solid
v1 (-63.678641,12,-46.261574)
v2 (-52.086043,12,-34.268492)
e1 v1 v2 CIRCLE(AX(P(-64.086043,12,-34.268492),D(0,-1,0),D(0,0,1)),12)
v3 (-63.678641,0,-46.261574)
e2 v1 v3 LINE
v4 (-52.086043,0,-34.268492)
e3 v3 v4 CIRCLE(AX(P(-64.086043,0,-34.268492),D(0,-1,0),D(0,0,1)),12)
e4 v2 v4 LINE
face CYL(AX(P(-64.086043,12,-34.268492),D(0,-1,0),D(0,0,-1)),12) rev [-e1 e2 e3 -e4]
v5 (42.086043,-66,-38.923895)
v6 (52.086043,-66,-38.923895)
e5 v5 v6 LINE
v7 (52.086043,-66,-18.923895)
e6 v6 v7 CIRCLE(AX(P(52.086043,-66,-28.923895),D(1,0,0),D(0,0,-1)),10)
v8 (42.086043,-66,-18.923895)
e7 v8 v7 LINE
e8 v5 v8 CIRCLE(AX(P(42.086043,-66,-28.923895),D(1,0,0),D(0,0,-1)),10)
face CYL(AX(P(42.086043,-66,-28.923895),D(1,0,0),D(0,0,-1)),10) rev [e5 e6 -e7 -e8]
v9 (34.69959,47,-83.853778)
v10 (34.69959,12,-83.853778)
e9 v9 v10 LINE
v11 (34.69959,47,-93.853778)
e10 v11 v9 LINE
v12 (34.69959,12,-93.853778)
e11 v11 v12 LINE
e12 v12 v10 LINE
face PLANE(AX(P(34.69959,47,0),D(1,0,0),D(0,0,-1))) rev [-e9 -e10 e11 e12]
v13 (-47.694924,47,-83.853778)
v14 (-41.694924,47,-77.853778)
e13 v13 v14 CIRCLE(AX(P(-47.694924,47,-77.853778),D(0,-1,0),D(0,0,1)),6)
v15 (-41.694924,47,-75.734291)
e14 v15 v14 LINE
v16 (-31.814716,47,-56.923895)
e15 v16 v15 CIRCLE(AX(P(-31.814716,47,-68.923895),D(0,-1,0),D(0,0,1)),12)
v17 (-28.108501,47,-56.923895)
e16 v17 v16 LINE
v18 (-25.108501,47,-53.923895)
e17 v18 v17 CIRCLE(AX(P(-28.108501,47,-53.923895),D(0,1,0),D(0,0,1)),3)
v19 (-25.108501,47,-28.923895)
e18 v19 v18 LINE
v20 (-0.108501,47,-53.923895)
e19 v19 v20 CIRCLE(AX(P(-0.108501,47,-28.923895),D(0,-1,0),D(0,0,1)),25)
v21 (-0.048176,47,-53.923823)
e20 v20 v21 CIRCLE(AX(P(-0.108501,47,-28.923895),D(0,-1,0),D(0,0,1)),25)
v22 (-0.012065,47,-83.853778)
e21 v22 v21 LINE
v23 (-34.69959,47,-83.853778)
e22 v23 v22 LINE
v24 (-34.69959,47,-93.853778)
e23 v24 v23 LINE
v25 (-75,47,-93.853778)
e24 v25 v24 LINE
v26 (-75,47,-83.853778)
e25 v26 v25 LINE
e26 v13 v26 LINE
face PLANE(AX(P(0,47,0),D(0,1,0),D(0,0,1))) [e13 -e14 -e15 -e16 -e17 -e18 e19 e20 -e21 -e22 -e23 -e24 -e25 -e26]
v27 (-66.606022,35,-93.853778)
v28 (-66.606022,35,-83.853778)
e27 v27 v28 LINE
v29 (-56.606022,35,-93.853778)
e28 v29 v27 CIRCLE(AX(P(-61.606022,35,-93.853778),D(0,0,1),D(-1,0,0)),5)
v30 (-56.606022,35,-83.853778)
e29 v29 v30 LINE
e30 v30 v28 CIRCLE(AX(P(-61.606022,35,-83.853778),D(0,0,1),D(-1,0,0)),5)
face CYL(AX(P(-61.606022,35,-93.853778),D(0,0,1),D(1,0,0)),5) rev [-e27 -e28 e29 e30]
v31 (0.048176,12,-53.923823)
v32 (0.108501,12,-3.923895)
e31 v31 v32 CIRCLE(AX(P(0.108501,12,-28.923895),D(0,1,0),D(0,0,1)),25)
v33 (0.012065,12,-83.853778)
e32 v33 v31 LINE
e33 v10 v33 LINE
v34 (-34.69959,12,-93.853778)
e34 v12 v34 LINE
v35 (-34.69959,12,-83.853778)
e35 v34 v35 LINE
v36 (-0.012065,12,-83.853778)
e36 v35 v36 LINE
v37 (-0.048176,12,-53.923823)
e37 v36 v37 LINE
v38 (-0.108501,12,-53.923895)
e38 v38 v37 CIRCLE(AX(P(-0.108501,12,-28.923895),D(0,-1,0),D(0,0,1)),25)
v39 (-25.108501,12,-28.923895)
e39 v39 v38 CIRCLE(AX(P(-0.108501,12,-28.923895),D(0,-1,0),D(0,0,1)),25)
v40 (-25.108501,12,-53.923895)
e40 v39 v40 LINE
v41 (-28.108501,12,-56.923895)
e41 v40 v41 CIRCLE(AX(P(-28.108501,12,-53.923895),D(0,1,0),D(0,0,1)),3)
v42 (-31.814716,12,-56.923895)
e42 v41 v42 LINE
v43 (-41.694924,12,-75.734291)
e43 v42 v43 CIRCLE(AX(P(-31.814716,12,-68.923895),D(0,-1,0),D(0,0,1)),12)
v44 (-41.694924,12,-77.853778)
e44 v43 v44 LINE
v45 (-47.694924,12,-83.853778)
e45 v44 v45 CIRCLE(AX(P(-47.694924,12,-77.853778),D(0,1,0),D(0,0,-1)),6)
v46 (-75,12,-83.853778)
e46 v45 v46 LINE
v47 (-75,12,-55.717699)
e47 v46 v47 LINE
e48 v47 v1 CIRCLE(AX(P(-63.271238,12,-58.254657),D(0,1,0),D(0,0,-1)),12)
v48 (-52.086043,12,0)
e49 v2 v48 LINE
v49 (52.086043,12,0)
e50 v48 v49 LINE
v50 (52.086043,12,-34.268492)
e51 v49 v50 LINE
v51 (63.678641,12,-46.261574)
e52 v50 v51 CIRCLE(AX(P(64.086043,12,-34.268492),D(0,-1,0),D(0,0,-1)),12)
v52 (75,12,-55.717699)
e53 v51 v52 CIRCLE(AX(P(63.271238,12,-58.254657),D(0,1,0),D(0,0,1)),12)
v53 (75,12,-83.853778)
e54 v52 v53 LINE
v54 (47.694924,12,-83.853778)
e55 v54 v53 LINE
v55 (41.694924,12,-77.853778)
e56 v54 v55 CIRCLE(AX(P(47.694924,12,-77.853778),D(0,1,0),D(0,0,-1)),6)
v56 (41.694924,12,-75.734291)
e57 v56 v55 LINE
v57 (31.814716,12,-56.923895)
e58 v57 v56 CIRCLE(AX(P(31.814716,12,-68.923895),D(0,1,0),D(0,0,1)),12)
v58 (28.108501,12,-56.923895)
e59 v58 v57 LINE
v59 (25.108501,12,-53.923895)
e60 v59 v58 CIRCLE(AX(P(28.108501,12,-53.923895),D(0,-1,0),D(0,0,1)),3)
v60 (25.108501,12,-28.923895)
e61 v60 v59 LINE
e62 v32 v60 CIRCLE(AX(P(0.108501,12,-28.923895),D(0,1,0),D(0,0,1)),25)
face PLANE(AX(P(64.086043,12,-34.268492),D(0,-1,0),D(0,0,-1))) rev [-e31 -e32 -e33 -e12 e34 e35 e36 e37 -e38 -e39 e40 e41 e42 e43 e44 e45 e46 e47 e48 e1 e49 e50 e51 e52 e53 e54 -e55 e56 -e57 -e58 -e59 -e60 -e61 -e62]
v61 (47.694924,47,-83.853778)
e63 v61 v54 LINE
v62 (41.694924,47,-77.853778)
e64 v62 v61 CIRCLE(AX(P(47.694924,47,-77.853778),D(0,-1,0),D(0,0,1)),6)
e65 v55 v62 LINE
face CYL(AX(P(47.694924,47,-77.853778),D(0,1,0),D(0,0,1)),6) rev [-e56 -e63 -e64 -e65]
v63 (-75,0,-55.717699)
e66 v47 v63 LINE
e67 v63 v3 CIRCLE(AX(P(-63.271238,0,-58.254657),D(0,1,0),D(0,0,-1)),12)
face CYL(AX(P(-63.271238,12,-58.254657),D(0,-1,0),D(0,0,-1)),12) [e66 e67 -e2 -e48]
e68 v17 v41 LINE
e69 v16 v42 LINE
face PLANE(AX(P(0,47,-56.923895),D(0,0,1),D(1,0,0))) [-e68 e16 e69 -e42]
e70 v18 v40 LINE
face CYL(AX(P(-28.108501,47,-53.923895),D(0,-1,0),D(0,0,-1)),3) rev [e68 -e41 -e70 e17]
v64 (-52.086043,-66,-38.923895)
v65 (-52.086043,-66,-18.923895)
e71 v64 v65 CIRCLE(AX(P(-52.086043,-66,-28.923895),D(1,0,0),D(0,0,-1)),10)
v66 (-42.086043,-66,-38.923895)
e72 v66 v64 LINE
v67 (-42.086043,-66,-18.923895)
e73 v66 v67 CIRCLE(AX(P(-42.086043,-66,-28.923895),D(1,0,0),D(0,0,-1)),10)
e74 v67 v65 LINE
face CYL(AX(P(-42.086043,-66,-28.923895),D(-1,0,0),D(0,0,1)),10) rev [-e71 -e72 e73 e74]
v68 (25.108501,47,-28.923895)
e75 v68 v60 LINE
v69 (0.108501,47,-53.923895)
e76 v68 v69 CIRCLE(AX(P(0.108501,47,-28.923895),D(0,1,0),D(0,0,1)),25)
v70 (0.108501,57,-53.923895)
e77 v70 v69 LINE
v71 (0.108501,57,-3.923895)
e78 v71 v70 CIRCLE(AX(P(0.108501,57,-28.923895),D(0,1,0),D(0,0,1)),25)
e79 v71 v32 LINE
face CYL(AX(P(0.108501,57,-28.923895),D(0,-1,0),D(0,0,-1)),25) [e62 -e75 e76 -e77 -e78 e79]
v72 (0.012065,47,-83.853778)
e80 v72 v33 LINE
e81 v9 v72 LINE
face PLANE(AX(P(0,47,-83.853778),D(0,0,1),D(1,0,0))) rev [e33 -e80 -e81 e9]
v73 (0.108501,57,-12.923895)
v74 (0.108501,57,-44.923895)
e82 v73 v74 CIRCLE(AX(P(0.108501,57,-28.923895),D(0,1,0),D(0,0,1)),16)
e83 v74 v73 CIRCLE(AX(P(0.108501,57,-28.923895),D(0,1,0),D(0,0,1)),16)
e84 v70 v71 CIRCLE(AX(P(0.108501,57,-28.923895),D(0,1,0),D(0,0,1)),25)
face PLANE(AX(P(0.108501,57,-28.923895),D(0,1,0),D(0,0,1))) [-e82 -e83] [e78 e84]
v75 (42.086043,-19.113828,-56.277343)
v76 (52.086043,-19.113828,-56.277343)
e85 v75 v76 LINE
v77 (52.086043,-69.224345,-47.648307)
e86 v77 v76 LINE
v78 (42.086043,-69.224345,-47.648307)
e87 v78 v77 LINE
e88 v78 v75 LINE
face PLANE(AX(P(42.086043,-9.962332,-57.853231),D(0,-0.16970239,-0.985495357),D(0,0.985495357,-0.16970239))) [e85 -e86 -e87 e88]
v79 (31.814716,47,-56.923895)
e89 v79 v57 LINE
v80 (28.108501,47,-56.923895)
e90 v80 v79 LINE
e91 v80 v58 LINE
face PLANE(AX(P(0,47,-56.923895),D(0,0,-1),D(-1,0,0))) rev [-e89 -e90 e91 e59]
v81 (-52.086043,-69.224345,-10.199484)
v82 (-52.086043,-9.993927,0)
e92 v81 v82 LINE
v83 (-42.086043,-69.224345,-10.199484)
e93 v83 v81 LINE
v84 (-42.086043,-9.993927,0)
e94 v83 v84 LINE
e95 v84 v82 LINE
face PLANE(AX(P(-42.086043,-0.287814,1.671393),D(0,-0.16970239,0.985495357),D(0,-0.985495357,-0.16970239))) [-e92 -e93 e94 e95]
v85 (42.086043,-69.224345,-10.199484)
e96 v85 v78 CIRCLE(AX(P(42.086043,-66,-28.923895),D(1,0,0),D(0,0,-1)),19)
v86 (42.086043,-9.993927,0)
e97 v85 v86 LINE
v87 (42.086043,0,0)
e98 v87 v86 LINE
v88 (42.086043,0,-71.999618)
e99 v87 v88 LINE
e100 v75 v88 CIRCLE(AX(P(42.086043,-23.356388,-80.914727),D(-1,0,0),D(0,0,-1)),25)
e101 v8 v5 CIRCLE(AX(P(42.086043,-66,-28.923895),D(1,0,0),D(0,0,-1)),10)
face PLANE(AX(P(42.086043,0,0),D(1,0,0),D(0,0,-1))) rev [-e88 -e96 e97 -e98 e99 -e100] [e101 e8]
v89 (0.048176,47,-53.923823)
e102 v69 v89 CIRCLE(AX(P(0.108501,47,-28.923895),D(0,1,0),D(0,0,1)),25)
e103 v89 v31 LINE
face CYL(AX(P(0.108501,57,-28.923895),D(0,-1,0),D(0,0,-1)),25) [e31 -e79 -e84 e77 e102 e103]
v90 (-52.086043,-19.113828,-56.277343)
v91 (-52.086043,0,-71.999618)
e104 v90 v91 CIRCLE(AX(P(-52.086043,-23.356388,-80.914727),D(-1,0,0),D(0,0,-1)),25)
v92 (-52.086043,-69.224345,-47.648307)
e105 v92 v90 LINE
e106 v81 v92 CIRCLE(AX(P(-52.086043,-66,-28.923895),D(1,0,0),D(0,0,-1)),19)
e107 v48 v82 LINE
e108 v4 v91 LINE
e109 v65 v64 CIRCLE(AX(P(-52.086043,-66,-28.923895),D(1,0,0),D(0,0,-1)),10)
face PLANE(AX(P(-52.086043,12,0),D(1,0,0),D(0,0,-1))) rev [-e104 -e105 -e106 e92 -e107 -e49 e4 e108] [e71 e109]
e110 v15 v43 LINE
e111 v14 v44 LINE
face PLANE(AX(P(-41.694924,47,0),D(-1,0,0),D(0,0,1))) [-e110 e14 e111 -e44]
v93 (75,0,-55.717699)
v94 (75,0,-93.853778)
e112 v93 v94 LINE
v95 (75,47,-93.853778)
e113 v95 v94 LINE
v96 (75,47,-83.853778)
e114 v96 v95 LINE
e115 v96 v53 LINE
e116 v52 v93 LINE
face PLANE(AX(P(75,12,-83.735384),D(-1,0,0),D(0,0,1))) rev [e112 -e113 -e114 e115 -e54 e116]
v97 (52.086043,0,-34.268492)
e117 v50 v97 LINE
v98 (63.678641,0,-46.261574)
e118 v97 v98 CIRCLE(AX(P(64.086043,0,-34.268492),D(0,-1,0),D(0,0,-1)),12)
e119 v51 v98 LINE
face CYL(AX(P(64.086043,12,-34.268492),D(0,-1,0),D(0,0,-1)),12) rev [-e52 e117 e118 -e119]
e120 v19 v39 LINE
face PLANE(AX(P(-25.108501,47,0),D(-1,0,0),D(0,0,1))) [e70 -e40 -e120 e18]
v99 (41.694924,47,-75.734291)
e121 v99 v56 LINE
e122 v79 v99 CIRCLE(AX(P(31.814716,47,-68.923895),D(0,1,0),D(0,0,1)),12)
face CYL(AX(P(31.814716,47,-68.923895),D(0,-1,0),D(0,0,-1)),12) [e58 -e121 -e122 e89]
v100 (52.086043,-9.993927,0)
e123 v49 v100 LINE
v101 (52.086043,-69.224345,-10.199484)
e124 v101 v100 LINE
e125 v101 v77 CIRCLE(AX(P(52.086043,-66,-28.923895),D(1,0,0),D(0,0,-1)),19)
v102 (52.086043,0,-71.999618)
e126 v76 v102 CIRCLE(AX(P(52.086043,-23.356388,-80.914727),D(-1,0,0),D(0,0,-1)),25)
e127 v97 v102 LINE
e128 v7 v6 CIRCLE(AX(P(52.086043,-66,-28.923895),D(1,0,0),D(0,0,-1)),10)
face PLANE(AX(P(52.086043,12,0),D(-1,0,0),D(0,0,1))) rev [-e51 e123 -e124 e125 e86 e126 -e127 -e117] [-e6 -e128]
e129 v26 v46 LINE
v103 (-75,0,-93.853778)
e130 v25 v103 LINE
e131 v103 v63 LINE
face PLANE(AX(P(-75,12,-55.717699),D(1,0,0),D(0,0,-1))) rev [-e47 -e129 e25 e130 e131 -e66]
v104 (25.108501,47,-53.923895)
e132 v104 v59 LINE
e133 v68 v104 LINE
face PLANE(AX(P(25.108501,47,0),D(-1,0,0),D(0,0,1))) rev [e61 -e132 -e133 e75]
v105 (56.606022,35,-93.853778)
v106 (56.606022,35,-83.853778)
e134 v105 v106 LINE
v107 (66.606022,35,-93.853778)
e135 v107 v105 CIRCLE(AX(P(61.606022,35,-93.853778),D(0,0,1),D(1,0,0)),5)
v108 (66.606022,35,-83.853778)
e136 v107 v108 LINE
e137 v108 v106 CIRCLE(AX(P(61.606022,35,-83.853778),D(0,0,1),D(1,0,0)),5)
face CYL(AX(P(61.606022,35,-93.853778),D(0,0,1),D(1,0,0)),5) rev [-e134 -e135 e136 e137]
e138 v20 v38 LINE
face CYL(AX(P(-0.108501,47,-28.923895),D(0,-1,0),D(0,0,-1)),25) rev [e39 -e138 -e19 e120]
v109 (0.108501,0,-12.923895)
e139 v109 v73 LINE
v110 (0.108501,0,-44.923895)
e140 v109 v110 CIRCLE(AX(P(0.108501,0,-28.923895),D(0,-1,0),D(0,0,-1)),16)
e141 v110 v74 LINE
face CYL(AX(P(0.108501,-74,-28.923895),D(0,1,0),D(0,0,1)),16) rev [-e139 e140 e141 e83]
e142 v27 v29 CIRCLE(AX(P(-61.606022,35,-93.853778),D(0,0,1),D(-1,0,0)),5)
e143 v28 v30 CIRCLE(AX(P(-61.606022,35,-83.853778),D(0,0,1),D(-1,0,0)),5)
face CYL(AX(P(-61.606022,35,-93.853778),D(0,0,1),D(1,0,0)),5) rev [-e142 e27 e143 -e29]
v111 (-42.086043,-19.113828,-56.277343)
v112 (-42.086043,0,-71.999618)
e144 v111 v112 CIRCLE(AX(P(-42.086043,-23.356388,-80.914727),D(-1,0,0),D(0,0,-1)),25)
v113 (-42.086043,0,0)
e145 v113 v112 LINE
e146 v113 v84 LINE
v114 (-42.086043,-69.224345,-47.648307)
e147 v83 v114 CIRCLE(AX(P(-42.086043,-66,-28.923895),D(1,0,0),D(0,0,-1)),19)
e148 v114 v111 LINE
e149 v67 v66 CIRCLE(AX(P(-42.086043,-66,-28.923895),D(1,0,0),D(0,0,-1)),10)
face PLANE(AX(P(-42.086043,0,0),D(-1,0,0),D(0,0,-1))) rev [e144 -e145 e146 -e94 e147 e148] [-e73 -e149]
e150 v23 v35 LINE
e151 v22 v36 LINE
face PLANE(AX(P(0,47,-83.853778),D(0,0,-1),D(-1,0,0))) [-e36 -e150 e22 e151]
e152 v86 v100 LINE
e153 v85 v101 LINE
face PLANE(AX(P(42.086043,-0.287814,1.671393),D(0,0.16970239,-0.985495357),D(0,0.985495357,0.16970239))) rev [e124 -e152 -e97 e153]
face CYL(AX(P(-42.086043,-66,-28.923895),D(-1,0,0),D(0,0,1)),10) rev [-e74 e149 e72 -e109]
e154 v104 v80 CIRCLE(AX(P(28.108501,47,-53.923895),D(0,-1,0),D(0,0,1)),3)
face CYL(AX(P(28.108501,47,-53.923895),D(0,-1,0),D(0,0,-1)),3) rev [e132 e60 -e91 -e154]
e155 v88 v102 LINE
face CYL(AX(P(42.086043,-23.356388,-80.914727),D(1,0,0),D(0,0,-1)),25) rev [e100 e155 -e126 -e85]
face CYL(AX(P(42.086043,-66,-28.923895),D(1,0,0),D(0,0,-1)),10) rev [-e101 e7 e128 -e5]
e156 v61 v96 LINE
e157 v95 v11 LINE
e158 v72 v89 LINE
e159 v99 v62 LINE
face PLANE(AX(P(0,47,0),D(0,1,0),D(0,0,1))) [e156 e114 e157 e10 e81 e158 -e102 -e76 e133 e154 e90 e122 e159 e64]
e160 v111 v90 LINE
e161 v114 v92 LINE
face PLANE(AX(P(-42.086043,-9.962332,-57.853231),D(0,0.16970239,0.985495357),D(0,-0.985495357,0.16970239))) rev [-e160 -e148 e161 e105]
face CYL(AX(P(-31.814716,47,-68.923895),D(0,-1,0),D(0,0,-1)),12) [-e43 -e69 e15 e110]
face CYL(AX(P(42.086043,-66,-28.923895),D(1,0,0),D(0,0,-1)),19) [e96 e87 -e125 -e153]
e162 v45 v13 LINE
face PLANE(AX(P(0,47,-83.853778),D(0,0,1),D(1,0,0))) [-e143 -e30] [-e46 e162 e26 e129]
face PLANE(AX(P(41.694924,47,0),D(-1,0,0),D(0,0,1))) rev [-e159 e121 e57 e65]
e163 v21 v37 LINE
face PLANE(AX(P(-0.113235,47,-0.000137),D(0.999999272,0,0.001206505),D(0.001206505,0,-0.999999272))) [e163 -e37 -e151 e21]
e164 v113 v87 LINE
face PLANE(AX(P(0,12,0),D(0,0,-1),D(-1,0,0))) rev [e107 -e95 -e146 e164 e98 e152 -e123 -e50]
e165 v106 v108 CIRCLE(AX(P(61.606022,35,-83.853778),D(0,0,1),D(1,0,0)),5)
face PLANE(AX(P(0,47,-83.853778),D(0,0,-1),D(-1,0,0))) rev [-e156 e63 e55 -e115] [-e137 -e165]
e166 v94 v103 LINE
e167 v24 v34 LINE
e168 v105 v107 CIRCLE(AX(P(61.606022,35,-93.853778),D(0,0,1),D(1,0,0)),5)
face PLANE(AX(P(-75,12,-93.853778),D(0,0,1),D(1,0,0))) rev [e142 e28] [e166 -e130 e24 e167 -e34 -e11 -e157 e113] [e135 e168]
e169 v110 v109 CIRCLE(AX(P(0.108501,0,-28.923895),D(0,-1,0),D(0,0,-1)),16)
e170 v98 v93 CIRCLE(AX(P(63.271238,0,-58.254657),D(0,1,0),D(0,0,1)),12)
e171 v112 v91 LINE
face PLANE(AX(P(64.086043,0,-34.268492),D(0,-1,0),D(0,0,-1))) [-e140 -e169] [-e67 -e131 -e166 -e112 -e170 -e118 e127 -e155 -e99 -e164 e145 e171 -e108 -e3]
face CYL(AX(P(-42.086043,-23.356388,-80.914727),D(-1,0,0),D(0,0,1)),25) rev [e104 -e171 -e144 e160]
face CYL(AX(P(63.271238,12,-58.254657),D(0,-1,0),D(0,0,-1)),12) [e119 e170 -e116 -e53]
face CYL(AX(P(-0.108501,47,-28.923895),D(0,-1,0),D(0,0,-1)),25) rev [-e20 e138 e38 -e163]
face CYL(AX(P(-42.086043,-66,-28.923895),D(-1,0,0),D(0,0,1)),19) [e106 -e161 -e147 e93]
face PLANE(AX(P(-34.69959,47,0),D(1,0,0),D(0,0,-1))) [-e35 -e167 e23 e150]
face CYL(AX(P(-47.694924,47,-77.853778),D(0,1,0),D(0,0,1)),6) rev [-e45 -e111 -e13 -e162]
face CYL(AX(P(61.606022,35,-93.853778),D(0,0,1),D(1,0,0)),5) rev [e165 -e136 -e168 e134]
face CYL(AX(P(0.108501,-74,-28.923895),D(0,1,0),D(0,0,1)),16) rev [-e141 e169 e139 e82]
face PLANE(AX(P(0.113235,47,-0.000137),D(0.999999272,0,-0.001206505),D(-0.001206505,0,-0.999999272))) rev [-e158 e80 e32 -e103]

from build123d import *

# Parameters (mm, degrees)
BASE_PLATE_DEPTH         = 12
LUG_DEPTH                = 35
BOSS_SKETCH_R            = 25
CYLINDRICAL_BOSS_DEPTH   = 45
LUG_FILLET_R6_R          = 6
MIRRORED_LUG_FILLET_R6_R = 6
BOSS_BORE_SKETCH_R       = 16
BOSS_BORE_DEPTH          = 131
SIDE_EAR_SKETCH_R        = 10.000000003
SIDE_EAR_DEPTH           = 10
RELIEF_CUT_SKETCH_R      = 5
RELIEF_CUT_DEPTH         = 10


with BuildPart() as part:
    # Base Plate Sketch → Base Plate (new body)
    with BuildSketch(Plane(origin=(0, 0, 0), x_dir=(1, 0, 0), z_dir=(0, 1, 0))):
        with BuildLine():
            Line((0, 0), (52.086042587, 0))
            Line((52.086042587, 0), (52.086042587, 34.268491931))
            ThreePointArc((52.086042587, 34.268491931), (55.457925039, 42.608491187), (63.678640518, 46.261574252))
            ThreePointArc((63.678640518, 46.261574252), (70.963844757, 49.044672415), (75, 55.717699243))
            Line((75, 55.717699243), (75, 83.735383518))
            Line((75, 83.735383518), (75, 93.85377774))
            Line((75, 93.85377774), (20.146433568, 93.85377774))
            Line((20.146433568, 93.85377774), (-75, 93.85377774))
            Line((-75, 93.85377774), (-75, 83.735383518))
            Line((-75, 83.735383518), (-75, 55.717699243))
            ThreePointArc((-75, 55.717699243), (-70.963844757, 49.044672415), (-63.678640518, 46.261574252))
            ThreePointArc((-63.678640518, 46.261574252), (-55.457925039, 42.608491187), (-52.086042587, 34.268491931))
            Line((-52.086042587, 34.268491931), (-52.086042587, 0))
            Line((-52.086042587, 0), (0, 0))
        make_face()
    extrude(amount=BASE_PLATE_DEPTH)

    # Lug Sketch → Lug (add)
    with BuildSketch(Plane(origin=(0, 12, 0), x_dir=(1, 0, 0), z_dir=(0, 1, 0))):
        with BuildLine():
            ThreePointArc((0.048175719, 53.923822509), (17.764829386, 46.622880149), (25.108500916, 28.923895292))
            Line((25.108500916, 28.923895292), (25.108500916, 53.923895292))
            ThreePointArc((25.108500916, 53.923895292), (25.987180573, 56.045215635), (28.108500916, 56.923895292))
            Line((28.108500916, 56.923895292), (31.814716412, 56.923895292))
            ThreePointArc((31.814716412, 56.923895292), (42.43838692, 63.34378553), (41.694924329, 75.734291134))
            Line((41.694924329, 75.734291134), (41.694924329, 83.85377774))
            Line((41.694924329, 83.85377774), (75, 83.85377774))
            Line((75, 83.85377774), (75, 93.85377774))
            Line((75, 93.85377774), (41.694924329, 93.85377774))
            Line((41.694924329, 93.85377774), (34.699589824, 93.85377774))
            Line((34.699589824, 93.85377774), (34.699589824, 83.85377774))
            Line((34.699589824, 83.85377774), (0.012065057, 83.85377774))
            Line((0.012065057, 83.85377774), (0.048175719, 53.923822509))
        make_face()
    lug = extrude(amount=LUG_DEPTH)

    # Lug Mirror: Lug across plane
    add(lug.mirror(Plane(origin=(0, 0, 0), x_dir=(0, 0, 1), z_dir=(1, 0, 0))))

    # Boss Sketch → Cylindrical Boss (add)
    with BuildSketch(Plane(origin=(0, 12, 0), x_dir=(1, 0, 0), z_dir=(0, 1, 0))):
        with Locations(Location((0.108500916, 28.923895292, 0), (0, 0, 90.138255303))):
            Circle(BOSS_SKETCH_R)
    extrude(amount=CYLINDRICAL_BOSS_DEPTH)

    # Lug Fillet R6
    lug_fillet_r6_edges = [part.edges().sort_by_distance(p)[0] for p in [
        (41.694924329, 29.5, -83.85377774),
    ]]
    fillet(lug_fillet_r6_edges, radius=LUG_FILLET_R6_R)

    # Mirrored Lug Fillet R6
    mirrored_lug_fillet_r6_edges = [part.edges().sort_by_distance(p)[0] for p in [
        (-41.694924329, 29.5, -83.85377774),
    ]]
    fillet(mirrored_lug_fillet_r6_edges, radius=MIRRORED_LUG_FILLET_R6_R)

    # Boss Bore Sketch → Boss Bore (cut)
    with BuildSketch(Plane(origin=(0, 57, 0), x_dir=(1, 0, 0), z_dir=(0, 1, 0))):
        with Locations(Location((0.108500916, 28.923895292, 0), (0, 0, 270))):
            Circle(BOSS_BORE_SKETCH_R)
    extrude(amount=-BOSS_BORE_DEPTH, mode=Mode.SUBTRACT)

    # Side Ear Sketch → Side Ear (add)
    with BuildSketch(Plane(origin=(52.086042587, 0, 0), x_dir=(0, 0, -1), z_dir=(1, 0, 0))):
        with BuildLine():
            Line((0, 0), (0, -9.993926671))
            Line((0, -9.993926671), (10.199483508, -69.224345425))
            ThreePointArc((10.199483505, -69.224345426), (28.923895292, -85.000000013), (47.648307078, -69.224345426))
            Line((47.648307075, -69.224345425), (56.277342763, -19.113827886))
            ThreePointArc((56.277342763, -19.113827886), (61.607291904, -7.474858686), (71.999618374, 0))
            Line((71.999618374, 0), (0, 0))
        make_face()
        with Locations((28.923895292, -66.00000001)):
            Circle(SIDE_EAR_SKETCH_R, mode=Mode.SUBTRACT)
    side_ear = extrude(amount=-SIDE_EAR_DEPTH)

    # Side Ear Mirror: Side Ear across plane
    add(side_ear.mirror(Plane(origin=(0, 0, 0), x_dir=(0, 0, 1), z_dir=(1, 0, 0))))

    # Relief Cut Sketch → Relief Cut (cut)
    with BuildSketch(Plane.XY.offset(-83.85377774)):
        with Locations((61.606022049, 35)):
            Circle(RELIEF_CUT_SKETCH_R)
        with Locations(Location((-61.606022049, 35, 0), (0, 0, 180))):
            Circle(RELIEF_CUT_SKETCH_R)
    extrude(amount=-RELIEF_CUT_DEPTH, mode=Mode.SUBTRACT)


solid = part.part
